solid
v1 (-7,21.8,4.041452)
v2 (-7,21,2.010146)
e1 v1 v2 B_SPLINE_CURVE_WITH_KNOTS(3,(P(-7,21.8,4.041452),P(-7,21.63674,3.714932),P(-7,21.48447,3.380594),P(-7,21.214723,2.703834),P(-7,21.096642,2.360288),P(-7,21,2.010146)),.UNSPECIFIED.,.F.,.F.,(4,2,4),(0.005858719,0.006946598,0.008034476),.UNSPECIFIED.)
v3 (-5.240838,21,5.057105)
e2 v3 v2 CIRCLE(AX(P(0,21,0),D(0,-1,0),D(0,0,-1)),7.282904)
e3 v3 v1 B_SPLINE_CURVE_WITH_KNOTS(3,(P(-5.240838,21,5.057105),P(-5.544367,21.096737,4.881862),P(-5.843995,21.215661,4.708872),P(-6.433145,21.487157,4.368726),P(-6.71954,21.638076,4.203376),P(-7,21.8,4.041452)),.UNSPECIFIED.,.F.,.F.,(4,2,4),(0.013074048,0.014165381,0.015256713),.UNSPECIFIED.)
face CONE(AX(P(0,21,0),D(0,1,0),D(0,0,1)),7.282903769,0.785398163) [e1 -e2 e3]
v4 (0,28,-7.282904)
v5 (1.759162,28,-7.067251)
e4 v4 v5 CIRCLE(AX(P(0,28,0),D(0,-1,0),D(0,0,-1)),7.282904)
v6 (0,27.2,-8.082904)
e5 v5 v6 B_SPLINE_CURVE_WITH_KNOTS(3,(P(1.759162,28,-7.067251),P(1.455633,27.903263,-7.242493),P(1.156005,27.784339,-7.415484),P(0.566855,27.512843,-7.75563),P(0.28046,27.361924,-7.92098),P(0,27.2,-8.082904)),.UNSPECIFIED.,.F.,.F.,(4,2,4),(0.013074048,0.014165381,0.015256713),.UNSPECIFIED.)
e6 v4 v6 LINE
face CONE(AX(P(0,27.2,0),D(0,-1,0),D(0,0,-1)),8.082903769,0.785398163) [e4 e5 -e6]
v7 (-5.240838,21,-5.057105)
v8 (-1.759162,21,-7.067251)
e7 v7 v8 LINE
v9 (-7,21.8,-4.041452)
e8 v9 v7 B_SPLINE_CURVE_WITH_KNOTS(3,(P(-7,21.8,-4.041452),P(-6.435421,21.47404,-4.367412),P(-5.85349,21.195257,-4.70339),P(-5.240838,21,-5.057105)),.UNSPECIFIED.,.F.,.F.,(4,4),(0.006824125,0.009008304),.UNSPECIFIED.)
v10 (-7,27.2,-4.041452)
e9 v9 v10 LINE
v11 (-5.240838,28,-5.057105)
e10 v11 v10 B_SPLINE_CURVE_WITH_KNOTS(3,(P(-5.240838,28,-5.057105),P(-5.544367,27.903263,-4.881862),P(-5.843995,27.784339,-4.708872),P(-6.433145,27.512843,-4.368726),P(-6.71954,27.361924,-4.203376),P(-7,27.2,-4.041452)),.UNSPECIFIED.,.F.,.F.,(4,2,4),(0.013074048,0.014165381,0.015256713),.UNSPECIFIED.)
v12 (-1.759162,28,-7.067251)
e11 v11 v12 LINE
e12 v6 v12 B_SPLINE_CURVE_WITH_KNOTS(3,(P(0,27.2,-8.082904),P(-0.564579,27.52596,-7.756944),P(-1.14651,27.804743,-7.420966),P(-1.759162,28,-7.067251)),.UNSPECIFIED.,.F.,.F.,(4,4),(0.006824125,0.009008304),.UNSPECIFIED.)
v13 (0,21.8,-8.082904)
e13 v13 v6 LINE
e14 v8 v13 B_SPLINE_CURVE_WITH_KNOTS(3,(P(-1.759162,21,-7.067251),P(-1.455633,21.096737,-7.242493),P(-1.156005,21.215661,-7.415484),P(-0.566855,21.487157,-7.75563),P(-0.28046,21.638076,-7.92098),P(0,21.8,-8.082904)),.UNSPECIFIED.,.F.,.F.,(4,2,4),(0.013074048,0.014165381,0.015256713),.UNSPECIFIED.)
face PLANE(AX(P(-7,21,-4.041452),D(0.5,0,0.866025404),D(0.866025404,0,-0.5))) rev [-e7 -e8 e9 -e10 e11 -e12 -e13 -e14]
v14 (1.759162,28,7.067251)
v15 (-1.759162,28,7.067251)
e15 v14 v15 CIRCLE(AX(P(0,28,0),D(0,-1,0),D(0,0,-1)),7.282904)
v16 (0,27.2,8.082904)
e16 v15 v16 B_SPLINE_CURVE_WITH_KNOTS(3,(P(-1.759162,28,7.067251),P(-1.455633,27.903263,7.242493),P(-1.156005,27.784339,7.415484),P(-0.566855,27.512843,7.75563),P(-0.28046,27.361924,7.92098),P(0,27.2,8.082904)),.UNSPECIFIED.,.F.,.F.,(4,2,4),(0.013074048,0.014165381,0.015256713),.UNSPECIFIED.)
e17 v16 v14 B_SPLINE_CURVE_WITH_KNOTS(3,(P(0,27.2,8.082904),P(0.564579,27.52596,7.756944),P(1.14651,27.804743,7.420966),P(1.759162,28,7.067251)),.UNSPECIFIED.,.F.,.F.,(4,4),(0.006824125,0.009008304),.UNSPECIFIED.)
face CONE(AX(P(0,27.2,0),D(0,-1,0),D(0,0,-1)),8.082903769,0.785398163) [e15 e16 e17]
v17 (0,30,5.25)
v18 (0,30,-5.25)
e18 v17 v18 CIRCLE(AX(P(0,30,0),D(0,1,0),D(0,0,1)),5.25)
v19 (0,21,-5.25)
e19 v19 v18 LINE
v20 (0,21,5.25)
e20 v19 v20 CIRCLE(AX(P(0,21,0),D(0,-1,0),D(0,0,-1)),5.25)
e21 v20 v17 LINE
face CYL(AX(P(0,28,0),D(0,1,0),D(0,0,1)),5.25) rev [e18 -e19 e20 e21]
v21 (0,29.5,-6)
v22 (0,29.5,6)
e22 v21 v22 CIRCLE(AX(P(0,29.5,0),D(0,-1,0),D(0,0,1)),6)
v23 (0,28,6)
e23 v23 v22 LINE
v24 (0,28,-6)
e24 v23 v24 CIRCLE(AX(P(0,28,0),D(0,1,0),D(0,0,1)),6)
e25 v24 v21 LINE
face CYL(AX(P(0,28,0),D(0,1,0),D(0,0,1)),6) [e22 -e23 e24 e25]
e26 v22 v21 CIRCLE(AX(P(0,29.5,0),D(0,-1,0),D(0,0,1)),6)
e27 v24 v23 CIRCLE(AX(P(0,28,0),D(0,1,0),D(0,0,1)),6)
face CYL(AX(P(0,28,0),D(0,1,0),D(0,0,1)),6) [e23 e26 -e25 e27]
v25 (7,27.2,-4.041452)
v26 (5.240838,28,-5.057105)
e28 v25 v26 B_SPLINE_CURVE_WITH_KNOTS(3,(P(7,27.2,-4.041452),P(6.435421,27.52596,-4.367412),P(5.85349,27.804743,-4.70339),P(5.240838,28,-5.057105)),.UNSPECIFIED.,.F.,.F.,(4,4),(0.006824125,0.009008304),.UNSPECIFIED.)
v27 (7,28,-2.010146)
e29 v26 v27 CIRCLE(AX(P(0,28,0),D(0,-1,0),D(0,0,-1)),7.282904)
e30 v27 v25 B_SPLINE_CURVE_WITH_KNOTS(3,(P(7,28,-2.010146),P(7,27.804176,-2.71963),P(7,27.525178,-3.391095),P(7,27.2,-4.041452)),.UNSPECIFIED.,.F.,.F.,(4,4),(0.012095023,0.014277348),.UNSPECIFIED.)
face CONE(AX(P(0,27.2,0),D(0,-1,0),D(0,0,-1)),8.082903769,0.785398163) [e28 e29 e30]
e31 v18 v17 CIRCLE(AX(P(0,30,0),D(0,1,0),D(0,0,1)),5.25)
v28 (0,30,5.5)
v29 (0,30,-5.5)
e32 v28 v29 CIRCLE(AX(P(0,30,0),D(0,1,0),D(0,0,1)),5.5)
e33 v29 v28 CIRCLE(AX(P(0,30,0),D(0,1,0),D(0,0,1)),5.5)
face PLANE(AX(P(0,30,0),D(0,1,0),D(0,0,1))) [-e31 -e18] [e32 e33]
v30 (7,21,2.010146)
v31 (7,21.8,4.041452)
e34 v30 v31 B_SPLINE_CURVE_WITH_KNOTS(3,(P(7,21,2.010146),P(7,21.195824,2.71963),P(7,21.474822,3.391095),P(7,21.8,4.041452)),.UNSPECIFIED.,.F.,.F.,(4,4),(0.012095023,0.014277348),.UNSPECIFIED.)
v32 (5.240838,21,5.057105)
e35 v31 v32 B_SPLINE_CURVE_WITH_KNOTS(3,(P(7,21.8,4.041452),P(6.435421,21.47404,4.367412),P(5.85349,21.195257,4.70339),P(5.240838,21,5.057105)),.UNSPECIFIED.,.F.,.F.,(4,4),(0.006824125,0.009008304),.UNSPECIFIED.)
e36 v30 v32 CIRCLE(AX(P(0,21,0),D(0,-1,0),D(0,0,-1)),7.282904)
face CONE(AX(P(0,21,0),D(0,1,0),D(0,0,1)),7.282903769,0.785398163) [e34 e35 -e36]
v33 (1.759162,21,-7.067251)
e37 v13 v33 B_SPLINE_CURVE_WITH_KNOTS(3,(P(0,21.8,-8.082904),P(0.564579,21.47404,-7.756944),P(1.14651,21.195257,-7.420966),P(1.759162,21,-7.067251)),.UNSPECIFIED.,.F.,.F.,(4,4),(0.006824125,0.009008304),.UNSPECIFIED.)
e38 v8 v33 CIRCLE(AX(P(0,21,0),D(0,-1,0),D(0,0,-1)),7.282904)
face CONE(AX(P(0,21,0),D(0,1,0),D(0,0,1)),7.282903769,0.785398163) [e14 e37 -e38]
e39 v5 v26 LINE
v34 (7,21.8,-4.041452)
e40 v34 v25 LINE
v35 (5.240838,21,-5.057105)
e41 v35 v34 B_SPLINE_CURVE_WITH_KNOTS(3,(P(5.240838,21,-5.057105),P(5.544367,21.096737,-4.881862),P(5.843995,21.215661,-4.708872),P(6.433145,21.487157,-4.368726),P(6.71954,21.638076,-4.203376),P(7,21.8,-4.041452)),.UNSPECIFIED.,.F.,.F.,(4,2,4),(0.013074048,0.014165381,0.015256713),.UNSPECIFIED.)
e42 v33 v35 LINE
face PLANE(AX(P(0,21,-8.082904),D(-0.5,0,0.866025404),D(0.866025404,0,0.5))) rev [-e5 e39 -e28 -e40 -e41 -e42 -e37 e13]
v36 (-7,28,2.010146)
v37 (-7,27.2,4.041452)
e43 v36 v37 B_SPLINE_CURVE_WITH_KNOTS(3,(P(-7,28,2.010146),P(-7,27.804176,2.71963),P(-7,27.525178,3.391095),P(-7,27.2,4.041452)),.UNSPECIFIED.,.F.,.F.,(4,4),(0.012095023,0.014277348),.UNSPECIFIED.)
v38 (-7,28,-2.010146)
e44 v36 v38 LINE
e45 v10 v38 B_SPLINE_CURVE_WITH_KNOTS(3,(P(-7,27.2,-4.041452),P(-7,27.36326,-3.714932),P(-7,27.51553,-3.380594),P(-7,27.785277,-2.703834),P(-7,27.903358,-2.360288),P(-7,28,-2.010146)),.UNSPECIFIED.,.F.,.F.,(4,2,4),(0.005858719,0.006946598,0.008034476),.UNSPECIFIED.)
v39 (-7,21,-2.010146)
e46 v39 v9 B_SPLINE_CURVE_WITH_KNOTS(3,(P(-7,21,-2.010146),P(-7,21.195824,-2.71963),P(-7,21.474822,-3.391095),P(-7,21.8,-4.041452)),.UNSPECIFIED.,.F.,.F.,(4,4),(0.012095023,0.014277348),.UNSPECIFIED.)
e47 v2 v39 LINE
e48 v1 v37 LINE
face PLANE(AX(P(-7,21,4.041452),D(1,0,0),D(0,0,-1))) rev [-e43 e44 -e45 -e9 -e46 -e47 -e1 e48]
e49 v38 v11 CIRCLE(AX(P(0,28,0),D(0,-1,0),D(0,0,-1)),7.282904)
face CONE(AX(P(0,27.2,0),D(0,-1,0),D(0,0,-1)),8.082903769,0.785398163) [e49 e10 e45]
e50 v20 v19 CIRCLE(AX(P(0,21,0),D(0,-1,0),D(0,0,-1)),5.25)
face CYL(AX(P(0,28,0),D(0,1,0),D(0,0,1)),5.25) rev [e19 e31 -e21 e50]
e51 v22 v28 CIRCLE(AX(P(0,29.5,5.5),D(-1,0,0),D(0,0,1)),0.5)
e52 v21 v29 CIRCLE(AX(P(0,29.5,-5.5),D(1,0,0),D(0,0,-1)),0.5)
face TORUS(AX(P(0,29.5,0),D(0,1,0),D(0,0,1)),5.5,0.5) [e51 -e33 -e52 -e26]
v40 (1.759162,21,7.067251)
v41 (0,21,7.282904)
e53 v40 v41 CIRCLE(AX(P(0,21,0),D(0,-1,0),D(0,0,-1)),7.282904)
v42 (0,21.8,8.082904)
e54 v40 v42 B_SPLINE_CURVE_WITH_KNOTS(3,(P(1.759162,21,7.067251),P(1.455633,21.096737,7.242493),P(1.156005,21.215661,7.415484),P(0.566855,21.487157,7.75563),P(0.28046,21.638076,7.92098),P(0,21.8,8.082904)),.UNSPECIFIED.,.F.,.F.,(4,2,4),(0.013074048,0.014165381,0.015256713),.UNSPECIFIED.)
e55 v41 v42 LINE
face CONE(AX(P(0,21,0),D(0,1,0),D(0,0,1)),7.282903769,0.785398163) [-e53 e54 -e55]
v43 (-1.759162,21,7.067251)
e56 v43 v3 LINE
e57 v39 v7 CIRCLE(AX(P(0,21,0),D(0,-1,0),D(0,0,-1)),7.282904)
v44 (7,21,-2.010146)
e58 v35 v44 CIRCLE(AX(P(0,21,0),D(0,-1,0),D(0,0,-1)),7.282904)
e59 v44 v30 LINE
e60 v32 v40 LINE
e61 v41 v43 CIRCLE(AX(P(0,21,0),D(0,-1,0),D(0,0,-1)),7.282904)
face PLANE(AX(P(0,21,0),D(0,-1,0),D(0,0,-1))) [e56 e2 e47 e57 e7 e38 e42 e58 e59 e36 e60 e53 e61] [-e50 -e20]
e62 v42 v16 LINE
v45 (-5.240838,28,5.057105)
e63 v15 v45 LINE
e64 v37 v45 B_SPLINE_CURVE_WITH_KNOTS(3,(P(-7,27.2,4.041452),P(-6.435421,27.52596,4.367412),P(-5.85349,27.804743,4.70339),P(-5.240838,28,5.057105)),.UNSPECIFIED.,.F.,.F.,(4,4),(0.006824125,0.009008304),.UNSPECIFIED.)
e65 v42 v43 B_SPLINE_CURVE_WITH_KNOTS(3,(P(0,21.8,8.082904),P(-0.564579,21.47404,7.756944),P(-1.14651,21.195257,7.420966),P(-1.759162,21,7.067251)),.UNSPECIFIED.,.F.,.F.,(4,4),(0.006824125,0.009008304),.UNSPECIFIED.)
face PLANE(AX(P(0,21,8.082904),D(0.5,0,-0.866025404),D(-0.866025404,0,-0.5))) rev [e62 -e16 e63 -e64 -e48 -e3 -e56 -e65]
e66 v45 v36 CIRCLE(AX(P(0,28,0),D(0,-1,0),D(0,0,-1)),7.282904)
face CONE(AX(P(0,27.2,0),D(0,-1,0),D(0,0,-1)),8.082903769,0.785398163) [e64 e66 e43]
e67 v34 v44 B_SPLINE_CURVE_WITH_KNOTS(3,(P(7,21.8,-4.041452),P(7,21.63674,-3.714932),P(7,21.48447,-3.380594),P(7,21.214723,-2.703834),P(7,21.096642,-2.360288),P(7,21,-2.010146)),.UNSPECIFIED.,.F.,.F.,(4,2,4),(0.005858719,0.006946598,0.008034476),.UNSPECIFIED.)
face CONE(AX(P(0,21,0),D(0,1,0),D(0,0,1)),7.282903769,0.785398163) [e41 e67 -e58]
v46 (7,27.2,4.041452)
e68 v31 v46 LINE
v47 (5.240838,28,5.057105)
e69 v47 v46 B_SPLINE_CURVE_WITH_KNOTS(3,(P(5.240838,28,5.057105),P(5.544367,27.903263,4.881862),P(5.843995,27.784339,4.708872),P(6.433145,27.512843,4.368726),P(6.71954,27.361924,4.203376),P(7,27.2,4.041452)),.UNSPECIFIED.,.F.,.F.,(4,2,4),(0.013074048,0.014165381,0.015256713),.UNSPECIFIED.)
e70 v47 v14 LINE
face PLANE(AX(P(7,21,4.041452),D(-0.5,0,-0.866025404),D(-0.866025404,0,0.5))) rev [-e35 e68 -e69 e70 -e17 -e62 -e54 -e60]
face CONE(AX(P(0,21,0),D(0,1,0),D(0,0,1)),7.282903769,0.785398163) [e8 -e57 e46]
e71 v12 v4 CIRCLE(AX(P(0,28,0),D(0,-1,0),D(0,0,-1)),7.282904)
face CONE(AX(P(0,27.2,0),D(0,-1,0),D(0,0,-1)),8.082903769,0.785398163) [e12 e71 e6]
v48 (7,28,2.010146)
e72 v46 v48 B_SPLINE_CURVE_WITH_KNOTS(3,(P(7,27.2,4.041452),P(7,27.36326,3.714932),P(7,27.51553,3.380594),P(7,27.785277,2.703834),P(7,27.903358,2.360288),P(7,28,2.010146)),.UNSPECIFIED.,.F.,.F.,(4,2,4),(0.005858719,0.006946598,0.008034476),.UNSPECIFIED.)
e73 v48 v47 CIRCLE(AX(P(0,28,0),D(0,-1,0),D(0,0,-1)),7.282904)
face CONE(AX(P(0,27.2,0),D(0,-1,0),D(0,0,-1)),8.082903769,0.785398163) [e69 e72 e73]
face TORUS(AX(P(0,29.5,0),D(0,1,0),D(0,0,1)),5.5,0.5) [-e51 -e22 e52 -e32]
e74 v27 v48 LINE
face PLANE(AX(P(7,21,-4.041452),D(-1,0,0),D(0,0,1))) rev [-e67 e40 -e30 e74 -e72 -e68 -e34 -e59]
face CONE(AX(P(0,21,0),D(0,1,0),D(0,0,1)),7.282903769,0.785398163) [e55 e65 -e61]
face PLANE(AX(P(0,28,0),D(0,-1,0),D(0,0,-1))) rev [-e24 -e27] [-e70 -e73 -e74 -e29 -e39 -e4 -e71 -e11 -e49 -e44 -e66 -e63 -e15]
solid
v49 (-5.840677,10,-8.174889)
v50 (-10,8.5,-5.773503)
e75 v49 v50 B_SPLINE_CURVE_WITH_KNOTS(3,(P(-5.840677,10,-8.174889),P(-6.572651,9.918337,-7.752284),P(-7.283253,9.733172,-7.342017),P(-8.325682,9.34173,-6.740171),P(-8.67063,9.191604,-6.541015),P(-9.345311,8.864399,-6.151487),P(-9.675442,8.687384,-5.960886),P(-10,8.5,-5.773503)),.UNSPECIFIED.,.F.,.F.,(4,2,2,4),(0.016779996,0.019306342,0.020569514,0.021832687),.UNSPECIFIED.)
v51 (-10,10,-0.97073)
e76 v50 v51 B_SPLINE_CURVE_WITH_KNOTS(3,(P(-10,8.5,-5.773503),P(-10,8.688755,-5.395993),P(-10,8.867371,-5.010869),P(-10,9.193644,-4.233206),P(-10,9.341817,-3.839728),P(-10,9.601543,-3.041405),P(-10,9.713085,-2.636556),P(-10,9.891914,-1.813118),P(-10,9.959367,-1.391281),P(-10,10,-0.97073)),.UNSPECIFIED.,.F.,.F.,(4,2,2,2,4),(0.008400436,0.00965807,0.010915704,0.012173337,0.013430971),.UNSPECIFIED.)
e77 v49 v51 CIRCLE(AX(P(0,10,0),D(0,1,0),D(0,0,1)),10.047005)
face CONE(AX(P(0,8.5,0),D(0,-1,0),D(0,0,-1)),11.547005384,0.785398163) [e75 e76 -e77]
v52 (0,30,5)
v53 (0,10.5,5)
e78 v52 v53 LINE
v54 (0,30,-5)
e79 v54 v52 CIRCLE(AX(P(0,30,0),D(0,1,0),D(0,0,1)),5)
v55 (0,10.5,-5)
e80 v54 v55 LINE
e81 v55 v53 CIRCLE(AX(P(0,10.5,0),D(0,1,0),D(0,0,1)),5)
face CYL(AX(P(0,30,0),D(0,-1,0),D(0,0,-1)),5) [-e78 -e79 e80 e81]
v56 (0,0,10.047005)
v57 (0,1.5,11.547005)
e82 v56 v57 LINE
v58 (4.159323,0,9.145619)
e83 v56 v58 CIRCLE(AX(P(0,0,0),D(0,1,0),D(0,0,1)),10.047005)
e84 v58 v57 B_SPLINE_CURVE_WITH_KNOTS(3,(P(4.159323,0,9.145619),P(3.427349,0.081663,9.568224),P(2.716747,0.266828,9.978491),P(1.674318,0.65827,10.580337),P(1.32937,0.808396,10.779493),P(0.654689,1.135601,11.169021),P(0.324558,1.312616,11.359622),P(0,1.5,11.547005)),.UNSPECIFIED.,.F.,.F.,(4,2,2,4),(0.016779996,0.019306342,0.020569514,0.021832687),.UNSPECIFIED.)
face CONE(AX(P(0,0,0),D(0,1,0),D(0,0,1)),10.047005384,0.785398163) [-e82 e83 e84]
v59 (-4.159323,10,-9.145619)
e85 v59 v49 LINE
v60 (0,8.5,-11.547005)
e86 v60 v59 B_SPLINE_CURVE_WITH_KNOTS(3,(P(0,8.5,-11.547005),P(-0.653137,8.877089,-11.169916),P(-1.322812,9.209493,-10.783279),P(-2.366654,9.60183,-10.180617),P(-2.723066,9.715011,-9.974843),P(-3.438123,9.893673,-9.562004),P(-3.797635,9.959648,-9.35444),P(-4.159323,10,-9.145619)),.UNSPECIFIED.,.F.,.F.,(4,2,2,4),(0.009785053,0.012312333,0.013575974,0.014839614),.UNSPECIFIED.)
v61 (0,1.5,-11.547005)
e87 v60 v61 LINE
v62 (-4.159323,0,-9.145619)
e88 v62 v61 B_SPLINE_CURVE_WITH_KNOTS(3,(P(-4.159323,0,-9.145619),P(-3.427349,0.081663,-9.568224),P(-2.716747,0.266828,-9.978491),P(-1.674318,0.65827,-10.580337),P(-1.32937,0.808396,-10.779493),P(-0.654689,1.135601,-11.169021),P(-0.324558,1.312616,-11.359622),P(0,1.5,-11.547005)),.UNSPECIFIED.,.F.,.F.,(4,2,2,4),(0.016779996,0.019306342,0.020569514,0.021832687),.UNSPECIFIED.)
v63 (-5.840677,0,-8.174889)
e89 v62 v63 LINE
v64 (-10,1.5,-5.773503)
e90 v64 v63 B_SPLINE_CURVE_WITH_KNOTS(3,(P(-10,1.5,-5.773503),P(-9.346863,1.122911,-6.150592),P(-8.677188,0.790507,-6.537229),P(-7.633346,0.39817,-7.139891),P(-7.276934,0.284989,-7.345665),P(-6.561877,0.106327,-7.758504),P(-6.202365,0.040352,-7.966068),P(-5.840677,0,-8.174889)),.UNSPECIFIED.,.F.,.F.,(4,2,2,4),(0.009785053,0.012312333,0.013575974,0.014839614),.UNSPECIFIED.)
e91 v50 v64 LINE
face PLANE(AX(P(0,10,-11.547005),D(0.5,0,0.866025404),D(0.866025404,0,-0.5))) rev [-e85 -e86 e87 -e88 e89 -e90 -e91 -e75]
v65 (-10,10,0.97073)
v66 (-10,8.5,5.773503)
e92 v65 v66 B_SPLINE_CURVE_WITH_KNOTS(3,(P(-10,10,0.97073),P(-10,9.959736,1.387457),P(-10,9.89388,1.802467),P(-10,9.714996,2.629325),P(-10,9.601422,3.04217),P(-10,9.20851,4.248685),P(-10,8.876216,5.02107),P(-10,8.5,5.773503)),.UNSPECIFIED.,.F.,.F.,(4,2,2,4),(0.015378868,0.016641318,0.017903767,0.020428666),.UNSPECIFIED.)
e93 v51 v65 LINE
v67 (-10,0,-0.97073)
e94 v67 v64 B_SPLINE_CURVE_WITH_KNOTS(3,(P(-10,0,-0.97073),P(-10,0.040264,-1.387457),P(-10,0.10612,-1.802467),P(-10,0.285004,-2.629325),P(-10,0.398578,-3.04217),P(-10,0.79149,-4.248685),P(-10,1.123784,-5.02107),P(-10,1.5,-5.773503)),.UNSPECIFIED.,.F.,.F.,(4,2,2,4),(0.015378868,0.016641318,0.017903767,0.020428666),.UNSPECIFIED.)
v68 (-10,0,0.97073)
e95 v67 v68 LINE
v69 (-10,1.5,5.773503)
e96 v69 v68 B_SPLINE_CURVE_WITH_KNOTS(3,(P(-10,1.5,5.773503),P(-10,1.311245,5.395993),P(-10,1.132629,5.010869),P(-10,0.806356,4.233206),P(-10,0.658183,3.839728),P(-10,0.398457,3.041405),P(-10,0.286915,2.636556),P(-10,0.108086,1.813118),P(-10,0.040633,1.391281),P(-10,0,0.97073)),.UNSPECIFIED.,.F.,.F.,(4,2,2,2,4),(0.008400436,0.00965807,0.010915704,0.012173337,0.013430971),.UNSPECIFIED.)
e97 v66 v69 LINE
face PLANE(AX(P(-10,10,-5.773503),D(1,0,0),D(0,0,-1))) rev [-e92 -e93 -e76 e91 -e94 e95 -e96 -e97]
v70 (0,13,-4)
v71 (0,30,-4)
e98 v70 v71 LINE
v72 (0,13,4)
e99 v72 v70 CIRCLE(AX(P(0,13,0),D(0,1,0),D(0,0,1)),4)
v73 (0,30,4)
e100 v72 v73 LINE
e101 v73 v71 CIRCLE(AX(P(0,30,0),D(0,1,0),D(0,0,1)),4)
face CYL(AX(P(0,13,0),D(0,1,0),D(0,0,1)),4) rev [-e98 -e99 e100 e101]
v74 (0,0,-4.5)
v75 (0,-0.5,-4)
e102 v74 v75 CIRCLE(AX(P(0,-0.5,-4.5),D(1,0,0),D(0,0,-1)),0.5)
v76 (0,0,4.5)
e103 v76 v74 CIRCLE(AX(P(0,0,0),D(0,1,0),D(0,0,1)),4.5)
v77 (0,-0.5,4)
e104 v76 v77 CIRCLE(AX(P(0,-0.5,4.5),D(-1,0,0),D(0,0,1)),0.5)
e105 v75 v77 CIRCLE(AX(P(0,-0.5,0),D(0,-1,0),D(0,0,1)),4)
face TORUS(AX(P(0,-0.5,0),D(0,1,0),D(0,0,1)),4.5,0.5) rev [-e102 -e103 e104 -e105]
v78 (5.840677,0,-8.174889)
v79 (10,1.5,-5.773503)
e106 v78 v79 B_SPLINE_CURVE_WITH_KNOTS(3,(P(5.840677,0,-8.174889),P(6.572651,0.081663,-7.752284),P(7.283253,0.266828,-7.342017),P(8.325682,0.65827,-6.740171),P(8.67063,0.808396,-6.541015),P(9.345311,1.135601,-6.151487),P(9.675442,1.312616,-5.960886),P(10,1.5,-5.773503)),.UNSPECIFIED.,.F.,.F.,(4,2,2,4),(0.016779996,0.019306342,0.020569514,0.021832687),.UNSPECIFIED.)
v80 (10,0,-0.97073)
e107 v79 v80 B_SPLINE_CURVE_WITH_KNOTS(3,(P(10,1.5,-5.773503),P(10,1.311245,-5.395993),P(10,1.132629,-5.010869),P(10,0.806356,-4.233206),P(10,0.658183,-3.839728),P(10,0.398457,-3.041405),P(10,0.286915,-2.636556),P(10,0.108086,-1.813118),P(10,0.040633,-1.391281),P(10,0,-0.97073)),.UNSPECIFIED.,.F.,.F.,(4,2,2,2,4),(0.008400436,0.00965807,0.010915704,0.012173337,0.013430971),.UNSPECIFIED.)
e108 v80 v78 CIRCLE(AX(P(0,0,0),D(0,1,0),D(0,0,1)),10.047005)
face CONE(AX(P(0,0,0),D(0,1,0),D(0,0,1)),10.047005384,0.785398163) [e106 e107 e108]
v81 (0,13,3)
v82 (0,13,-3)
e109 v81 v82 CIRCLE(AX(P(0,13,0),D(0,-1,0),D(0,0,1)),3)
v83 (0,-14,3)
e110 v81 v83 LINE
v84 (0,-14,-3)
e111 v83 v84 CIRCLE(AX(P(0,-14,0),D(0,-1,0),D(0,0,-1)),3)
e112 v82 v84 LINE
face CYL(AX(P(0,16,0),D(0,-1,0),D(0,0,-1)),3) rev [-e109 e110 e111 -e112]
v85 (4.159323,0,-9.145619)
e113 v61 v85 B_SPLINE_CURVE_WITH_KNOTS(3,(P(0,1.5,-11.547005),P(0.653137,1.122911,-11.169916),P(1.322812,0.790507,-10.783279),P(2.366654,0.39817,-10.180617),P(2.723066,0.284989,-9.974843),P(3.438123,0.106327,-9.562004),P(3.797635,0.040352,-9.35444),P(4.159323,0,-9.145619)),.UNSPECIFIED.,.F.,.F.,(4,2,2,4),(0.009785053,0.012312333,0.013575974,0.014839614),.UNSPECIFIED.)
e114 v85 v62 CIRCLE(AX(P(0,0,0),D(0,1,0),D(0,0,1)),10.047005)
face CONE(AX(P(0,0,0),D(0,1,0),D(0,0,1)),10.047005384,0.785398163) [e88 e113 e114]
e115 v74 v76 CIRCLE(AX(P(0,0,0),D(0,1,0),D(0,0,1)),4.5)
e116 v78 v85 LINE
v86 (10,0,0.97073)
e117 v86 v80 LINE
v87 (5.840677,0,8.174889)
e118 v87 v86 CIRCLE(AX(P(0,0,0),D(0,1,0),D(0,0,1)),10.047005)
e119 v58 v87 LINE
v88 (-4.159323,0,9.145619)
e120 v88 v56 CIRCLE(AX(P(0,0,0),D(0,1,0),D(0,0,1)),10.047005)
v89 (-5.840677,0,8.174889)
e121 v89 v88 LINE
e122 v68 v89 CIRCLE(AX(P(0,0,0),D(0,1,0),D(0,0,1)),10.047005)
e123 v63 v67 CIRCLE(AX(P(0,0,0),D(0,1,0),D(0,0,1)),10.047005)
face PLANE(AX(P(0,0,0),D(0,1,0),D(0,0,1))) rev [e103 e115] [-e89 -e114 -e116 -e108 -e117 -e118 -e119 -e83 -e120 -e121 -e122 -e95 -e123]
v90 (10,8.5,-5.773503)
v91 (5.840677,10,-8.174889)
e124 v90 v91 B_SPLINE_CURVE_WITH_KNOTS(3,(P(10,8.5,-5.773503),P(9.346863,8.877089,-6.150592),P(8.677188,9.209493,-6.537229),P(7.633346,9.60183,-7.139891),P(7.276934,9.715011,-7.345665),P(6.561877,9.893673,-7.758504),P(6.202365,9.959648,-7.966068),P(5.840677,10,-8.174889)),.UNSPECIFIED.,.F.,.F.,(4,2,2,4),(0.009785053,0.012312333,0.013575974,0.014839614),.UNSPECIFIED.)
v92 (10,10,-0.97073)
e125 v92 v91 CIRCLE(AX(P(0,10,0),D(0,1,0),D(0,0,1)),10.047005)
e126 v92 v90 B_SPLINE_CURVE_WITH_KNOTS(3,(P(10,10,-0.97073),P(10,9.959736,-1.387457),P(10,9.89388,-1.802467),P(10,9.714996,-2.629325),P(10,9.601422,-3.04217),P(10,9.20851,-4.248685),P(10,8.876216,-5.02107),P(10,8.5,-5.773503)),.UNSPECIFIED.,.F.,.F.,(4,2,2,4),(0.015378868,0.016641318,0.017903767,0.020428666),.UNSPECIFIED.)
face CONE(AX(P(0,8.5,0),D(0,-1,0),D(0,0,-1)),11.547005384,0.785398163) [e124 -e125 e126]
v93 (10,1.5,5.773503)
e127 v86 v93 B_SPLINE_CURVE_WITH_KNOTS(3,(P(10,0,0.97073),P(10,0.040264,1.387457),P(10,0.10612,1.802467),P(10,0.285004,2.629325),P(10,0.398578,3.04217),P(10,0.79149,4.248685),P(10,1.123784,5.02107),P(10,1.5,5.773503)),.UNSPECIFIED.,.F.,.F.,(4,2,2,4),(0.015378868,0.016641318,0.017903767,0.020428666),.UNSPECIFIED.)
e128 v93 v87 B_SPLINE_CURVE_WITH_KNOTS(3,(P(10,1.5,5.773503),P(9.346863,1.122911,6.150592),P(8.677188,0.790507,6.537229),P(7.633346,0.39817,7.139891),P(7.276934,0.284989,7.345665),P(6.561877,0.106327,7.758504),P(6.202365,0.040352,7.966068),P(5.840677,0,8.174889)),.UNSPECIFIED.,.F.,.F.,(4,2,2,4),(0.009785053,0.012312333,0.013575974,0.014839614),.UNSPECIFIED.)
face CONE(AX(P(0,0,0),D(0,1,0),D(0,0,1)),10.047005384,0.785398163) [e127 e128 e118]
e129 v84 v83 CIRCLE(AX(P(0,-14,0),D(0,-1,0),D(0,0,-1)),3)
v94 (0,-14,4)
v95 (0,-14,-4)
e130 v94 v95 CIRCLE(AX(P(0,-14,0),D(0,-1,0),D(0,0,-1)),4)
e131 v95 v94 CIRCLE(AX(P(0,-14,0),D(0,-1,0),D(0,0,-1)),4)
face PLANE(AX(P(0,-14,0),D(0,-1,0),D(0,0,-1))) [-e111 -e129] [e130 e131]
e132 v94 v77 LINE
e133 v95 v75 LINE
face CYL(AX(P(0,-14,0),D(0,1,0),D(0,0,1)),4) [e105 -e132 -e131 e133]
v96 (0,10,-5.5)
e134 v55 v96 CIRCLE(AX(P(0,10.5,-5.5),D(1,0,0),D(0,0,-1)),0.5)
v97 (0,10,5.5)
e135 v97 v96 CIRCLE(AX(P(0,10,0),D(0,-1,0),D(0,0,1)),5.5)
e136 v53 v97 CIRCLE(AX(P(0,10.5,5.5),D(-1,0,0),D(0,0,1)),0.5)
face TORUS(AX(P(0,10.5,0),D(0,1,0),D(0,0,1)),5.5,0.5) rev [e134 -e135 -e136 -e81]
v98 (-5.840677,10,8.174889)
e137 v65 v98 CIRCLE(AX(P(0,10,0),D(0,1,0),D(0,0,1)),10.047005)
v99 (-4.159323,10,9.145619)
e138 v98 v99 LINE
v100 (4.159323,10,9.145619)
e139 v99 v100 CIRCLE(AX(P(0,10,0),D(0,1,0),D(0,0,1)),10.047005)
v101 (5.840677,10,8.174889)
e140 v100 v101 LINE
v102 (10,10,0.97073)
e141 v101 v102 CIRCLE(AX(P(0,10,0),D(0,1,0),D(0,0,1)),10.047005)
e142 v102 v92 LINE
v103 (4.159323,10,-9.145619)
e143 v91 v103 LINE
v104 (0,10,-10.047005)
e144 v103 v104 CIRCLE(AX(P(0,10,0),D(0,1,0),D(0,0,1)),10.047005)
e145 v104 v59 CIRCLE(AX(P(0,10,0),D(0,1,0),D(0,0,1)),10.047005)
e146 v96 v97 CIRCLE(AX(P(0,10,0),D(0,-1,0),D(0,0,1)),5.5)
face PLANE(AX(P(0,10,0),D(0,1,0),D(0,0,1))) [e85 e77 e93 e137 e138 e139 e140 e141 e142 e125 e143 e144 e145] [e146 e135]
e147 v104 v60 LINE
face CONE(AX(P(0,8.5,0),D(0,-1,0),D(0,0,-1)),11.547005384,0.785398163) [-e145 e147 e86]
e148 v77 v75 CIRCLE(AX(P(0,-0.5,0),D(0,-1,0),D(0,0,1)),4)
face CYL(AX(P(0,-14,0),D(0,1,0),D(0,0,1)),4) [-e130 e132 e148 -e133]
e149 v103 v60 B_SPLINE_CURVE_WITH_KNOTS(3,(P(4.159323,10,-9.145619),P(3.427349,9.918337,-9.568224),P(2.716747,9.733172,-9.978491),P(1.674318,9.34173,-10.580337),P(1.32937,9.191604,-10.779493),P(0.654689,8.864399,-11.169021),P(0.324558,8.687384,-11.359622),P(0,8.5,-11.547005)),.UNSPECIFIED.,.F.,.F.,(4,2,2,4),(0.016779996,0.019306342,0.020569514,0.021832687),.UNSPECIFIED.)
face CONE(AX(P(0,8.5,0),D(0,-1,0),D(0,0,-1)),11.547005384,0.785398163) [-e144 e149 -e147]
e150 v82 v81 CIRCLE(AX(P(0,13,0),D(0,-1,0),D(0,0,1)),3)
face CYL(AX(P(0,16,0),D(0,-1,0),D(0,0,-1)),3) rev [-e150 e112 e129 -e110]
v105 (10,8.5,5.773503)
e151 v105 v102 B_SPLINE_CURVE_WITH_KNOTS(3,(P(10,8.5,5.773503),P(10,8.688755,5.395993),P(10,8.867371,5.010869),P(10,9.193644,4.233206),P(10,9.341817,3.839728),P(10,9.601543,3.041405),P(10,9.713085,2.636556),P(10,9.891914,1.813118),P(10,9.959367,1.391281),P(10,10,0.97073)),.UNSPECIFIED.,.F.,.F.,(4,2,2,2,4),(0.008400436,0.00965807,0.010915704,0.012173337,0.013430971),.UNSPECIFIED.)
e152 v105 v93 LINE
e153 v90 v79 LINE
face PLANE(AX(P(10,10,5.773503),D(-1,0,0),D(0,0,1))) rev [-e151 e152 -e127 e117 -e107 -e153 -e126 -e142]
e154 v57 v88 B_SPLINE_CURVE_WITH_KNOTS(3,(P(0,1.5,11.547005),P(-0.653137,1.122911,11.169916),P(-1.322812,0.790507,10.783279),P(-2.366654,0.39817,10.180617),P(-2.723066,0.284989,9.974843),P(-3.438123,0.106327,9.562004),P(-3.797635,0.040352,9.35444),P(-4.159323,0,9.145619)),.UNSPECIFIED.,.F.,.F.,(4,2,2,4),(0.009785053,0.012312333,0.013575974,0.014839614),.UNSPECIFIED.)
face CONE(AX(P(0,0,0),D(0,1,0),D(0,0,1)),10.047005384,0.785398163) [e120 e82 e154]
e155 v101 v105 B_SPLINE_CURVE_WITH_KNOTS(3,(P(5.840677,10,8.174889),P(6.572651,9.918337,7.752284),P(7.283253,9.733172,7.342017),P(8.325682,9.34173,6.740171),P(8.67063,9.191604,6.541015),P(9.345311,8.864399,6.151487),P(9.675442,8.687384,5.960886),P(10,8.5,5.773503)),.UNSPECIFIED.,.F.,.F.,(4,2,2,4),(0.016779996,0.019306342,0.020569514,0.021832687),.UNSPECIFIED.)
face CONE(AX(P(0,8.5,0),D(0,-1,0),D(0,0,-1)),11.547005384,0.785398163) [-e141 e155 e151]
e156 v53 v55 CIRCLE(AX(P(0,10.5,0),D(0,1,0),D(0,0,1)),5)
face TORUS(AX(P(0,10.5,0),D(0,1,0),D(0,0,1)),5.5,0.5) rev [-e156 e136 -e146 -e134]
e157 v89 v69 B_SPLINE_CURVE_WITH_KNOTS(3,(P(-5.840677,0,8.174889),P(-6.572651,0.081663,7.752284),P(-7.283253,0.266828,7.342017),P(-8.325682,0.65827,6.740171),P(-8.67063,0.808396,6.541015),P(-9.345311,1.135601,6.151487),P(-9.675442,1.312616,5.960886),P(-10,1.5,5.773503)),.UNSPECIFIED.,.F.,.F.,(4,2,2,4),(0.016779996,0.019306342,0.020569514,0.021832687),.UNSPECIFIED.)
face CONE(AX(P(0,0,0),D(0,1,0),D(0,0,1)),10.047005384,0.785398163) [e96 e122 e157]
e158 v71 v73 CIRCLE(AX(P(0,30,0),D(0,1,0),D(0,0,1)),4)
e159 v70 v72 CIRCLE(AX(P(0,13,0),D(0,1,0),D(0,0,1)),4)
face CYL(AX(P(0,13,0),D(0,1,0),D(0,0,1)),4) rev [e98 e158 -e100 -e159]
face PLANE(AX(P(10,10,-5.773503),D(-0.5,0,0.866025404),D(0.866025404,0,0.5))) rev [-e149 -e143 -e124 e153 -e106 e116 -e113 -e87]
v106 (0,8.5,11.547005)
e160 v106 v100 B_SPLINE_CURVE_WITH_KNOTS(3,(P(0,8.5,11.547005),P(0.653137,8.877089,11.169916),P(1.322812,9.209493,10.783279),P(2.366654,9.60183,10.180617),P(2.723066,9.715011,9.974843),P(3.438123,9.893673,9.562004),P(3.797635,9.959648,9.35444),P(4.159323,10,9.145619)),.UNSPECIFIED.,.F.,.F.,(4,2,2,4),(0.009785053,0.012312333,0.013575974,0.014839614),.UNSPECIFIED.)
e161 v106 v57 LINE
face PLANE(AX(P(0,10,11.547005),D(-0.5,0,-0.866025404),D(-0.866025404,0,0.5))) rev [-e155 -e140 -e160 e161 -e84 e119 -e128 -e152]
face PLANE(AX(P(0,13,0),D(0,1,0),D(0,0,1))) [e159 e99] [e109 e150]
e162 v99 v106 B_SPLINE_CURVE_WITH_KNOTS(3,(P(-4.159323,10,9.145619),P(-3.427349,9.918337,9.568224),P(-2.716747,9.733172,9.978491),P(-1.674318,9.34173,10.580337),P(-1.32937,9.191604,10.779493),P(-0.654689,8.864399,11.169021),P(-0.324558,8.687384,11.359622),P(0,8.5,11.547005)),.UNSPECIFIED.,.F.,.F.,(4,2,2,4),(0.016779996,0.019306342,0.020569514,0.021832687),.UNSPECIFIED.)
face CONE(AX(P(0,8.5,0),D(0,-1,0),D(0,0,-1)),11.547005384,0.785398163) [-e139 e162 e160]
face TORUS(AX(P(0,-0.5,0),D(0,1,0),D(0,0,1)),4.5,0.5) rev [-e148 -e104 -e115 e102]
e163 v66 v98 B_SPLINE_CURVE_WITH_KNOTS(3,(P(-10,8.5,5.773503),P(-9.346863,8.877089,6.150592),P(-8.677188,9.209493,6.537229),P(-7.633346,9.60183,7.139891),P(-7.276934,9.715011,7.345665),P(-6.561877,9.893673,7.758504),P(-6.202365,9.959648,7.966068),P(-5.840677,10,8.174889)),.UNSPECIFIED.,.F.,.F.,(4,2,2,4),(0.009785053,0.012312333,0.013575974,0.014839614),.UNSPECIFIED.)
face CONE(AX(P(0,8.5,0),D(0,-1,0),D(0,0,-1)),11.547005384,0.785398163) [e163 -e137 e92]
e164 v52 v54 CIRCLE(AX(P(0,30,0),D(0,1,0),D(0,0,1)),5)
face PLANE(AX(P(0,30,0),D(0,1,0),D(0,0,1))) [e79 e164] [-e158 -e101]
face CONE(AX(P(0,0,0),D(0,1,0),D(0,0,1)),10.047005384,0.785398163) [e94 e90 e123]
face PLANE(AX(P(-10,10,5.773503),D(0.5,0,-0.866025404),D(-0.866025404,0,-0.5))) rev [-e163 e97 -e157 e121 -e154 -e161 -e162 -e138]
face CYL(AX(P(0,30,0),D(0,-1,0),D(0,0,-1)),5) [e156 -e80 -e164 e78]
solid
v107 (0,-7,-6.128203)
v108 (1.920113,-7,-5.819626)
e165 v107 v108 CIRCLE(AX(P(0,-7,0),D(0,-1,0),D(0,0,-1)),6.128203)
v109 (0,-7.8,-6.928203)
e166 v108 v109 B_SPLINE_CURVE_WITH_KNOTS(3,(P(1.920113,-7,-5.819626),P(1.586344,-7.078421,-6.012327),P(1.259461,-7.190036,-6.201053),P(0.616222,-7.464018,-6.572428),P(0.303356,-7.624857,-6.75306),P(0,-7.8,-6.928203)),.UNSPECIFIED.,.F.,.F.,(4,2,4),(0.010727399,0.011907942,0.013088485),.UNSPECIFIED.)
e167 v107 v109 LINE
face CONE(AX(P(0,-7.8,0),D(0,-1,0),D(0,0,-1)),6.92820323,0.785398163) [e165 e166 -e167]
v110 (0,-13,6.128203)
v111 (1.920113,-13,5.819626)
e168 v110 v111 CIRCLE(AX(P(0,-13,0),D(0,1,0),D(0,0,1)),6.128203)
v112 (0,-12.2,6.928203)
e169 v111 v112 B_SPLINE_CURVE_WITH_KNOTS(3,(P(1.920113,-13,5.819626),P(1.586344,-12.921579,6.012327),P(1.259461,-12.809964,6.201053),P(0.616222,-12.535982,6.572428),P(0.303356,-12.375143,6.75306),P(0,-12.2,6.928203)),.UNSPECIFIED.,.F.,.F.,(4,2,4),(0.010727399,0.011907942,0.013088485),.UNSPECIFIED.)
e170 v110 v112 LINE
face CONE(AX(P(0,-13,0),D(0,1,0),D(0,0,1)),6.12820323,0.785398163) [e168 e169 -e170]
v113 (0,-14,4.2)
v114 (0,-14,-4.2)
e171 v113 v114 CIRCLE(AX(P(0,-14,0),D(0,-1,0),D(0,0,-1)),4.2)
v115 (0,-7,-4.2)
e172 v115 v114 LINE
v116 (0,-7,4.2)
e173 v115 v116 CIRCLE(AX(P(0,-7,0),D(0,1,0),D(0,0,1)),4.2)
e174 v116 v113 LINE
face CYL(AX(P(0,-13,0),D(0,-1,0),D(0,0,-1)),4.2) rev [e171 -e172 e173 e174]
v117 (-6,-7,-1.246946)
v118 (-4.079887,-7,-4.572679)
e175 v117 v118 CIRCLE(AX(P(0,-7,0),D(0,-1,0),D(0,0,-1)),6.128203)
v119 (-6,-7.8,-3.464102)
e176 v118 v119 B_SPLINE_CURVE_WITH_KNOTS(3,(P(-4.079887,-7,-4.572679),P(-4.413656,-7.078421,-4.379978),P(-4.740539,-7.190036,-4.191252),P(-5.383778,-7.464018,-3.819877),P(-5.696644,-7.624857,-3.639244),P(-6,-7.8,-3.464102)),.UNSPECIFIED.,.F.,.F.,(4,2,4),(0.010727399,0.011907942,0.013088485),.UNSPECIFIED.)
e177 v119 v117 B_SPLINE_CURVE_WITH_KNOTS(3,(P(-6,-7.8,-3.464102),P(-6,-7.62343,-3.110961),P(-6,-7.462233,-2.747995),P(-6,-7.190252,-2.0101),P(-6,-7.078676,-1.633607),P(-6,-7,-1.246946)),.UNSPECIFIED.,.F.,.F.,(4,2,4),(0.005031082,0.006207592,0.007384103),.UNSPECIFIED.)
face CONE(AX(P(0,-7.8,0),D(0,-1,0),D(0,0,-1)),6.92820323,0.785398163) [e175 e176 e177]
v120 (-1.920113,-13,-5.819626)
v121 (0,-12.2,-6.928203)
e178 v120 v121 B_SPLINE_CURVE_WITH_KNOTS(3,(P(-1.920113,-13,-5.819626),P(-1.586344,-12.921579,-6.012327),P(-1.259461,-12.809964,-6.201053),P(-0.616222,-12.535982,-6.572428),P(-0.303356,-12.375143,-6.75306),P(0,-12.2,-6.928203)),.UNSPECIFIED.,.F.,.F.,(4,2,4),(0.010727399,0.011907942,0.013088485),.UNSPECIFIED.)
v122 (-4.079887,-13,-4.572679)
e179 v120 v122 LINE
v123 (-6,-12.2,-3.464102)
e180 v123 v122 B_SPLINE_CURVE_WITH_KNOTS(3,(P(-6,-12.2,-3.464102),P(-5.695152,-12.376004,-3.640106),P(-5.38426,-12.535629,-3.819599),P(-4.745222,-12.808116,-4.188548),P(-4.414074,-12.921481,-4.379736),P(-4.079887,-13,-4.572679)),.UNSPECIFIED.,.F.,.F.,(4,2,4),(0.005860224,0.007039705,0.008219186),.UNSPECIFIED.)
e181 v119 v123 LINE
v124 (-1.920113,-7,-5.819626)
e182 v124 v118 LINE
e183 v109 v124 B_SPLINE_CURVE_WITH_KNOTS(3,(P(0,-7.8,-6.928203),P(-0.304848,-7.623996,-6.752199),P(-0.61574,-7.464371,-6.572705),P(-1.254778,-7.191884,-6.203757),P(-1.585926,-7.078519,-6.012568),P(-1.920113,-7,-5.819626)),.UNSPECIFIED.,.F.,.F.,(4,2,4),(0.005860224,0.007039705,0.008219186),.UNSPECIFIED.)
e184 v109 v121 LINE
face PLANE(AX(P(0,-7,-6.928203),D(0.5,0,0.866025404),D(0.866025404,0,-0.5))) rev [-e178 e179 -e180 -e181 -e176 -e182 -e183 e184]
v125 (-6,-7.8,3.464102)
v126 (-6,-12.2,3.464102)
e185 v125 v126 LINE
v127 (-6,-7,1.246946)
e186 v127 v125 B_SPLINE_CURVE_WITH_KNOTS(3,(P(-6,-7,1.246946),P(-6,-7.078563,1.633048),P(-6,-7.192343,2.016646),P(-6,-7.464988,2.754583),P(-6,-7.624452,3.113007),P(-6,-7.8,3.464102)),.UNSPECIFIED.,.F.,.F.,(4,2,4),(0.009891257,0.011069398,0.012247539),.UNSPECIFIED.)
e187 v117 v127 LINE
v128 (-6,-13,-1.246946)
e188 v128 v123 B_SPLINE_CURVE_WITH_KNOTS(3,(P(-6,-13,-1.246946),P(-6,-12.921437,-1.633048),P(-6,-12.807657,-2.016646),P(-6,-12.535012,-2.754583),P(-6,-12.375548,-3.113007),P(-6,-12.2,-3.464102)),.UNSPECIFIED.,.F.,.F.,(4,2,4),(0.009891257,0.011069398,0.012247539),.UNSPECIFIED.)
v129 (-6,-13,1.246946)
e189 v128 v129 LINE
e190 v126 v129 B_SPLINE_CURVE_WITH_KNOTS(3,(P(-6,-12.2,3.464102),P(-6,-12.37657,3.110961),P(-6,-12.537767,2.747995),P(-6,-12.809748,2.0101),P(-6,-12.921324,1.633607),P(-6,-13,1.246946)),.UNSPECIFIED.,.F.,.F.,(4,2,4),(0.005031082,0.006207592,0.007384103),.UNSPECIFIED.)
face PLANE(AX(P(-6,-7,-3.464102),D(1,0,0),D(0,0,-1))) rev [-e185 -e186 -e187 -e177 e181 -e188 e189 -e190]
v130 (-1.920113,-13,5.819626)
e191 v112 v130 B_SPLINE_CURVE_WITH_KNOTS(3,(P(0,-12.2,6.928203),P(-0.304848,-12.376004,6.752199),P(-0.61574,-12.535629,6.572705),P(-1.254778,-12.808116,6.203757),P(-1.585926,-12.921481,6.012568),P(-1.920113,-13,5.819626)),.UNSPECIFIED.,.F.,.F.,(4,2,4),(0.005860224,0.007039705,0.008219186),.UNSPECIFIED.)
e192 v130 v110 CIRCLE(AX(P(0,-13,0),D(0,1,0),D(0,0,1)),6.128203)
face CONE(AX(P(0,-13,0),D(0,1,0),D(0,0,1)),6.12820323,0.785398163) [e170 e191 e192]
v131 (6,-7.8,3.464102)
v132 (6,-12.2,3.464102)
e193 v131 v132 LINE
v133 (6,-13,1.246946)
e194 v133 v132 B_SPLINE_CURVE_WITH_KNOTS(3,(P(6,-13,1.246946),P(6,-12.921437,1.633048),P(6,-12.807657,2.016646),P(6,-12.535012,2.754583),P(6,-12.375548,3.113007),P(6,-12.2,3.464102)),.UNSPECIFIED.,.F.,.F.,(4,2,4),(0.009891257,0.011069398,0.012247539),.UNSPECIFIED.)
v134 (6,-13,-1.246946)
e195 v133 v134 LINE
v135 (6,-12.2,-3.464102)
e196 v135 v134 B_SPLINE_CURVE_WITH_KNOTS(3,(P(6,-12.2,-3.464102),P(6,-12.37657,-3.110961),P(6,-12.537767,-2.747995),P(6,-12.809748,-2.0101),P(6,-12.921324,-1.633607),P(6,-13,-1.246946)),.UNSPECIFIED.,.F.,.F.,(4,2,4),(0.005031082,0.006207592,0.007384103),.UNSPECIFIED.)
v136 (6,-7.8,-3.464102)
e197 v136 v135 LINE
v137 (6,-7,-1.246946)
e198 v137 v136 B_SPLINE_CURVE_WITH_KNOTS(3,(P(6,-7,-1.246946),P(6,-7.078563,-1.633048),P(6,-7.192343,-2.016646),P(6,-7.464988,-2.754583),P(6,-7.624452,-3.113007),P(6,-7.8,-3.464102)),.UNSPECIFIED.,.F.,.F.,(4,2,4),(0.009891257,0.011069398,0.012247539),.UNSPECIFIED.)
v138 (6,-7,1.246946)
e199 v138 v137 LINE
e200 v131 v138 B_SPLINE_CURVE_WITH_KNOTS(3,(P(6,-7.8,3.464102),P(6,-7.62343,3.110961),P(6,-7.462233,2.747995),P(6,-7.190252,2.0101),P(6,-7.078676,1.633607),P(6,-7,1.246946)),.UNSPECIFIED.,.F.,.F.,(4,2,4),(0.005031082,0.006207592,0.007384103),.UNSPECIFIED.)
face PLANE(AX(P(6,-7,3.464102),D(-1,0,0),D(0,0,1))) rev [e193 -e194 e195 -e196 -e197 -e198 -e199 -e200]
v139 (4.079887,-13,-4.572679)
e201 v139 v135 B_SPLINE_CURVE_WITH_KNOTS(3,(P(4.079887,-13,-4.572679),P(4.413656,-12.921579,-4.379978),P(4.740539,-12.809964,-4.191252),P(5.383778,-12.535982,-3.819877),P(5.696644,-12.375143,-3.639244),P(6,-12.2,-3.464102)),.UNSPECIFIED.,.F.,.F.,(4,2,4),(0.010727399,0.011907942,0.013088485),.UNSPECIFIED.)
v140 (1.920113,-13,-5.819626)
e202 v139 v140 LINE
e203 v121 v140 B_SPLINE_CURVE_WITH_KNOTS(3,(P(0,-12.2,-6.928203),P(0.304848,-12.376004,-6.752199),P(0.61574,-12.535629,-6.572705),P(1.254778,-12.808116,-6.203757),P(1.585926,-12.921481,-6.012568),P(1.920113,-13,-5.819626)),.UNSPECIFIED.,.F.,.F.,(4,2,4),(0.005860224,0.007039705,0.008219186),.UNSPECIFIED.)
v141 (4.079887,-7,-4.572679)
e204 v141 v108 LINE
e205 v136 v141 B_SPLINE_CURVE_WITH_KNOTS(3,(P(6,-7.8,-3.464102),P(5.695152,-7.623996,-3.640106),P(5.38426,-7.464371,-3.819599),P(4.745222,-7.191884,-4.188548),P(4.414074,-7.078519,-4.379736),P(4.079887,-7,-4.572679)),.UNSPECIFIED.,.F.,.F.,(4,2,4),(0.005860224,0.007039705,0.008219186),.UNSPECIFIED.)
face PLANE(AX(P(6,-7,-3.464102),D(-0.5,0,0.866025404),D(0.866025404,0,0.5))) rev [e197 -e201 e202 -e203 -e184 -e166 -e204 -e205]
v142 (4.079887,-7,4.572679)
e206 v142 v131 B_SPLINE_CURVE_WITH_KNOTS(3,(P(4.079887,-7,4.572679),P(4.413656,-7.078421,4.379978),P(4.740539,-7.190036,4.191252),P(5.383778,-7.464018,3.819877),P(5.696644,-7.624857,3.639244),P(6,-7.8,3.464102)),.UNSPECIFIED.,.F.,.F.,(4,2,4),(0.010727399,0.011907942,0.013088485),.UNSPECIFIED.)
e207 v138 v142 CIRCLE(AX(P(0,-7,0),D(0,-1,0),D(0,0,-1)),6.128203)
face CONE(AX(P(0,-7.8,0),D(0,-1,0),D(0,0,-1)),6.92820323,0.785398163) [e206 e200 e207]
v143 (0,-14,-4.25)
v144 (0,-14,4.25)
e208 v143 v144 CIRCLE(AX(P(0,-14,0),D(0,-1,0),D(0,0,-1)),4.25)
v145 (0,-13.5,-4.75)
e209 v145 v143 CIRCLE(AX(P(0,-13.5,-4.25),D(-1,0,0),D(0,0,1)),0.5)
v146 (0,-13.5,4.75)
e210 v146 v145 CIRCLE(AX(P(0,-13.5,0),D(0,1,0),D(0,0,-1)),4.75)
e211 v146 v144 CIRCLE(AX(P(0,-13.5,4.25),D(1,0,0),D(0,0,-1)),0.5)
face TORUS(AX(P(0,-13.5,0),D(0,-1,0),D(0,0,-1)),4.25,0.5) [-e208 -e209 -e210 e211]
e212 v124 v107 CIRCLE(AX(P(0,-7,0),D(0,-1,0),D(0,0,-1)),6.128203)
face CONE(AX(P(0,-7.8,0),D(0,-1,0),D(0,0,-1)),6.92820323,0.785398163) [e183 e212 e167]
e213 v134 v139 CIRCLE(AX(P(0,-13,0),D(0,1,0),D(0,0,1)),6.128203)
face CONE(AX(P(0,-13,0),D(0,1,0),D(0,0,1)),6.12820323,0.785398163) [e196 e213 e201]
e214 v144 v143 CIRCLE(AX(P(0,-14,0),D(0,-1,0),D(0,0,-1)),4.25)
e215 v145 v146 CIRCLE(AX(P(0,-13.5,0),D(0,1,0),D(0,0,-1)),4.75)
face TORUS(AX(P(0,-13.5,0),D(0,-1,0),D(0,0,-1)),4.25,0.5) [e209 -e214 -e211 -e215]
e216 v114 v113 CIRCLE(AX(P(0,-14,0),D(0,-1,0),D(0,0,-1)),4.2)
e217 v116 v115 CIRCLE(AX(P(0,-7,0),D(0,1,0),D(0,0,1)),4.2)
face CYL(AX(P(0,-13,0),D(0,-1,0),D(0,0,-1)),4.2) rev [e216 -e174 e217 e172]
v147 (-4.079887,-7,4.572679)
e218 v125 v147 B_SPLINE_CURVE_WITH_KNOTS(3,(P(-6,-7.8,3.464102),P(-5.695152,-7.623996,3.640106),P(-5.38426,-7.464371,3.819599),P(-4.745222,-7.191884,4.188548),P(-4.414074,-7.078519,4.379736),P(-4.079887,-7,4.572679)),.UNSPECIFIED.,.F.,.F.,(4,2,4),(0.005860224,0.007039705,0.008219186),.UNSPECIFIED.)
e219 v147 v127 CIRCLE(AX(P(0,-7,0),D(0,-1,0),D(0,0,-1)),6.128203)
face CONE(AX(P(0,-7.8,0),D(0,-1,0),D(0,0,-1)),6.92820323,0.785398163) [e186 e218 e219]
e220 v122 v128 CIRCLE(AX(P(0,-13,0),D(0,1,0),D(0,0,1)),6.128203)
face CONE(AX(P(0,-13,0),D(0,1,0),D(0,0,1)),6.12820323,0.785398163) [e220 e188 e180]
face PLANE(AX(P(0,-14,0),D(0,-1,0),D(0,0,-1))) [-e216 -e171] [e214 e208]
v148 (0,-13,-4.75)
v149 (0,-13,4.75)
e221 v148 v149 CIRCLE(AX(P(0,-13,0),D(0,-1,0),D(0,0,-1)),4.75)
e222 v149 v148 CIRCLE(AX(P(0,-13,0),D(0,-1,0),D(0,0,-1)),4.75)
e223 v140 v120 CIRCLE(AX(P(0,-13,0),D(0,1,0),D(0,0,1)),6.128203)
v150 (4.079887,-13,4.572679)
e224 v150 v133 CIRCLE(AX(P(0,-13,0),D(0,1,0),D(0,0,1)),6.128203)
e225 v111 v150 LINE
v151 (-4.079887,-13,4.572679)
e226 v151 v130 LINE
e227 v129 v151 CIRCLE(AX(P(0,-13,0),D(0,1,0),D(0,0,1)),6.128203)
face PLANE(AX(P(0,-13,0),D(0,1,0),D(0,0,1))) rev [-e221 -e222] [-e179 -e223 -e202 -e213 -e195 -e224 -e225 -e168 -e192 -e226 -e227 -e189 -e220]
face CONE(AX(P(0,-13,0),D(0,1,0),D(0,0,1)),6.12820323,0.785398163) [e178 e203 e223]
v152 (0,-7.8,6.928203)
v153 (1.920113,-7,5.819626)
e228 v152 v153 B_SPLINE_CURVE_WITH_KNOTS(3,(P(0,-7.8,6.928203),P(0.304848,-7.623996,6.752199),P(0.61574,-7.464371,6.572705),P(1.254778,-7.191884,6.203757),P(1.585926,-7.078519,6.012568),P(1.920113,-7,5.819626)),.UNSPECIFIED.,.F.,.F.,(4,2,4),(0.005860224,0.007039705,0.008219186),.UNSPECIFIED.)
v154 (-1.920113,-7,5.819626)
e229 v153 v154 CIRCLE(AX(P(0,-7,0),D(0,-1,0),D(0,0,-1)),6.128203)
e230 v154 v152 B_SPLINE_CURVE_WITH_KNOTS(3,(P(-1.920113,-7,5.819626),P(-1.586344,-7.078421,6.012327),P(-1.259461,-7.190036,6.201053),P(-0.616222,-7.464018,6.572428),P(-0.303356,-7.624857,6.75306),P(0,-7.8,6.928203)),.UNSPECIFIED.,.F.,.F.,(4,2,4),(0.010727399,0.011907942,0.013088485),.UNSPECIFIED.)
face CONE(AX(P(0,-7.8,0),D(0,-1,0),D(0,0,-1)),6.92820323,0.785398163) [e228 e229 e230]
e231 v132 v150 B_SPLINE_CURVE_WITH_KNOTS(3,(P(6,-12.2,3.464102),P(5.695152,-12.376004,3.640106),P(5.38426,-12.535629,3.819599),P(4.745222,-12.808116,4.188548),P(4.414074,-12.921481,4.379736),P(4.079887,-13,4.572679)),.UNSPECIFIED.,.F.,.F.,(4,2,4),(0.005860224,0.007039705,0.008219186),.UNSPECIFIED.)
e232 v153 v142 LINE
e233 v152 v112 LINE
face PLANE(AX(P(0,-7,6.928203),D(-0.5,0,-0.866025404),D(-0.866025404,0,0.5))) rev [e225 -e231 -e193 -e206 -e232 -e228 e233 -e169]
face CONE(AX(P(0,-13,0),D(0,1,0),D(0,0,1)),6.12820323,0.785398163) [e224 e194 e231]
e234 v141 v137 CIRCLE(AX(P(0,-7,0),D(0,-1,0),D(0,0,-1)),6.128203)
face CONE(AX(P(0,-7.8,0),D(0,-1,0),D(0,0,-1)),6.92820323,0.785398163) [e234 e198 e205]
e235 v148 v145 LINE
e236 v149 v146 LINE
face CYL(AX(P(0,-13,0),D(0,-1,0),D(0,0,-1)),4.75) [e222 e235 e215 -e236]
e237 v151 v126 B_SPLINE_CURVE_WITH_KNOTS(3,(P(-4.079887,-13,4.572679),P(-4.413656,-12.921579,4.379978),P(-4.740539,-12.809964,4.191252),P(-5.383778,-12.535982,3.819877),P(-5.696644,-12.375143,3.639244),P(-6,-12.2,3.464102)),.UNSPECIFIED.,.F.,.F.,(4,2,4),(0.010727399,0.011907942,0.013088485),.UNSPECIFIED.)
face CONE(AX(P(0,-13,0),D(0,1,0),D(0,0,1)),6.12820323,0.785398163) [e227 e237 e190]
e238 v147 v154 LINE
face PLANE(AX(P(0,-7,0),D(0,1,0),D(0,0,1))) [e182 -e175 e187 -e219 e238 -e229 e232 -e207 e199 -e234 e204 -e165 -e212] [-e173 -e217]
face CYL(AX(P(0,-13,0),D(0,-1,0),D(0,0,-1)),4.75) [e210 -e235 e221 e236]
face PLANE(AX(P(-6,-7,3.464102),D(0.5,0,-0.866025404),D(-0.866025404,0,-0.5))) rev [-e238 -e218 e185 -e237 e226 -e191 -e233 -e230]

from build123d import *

# Parameters (mm, degrees)
BOSS_EXTRUDE1_DEPTH = 10
SKETCH2_R           = 5
BOSS_EXTRUDE2_DEPTH = 20
SKETCH3_R           = 4
BOSS_EXTRUDE3_DEPTH = 14
SKETCH4_R           = 3
CUT_EXTRUDE1_DEPTH  = 30
SKETCH5_R           = 4
CUT_EXTRUDE2_DEPTH  = 17
SKETCH6_R           = 6
SKETCH6_R_2         = 5.25
BOSS_EXTRUDE4_DEPTH = 2
SKETCH7_R           = 5.25
BOSS_EXTRUDE5_DEPTH = 7
SKETCH11_R          = 4.75
SKETCH11_R_2        = 4.2
BOSS_EXTRUDE6_DEPTH = 1
SKETCH12_R          = 4.2
BOSS_EXTRUDE7_DEPTH = 6
FILLET1_R           = 0.5
FILLET2_R           = 0.5
FILLET3_R           = 0.5


with BuildPart() as part:
    # Sketch1 → Boss-Extrude1 (new body)
    with BuildSketch(Plane(origin=(0, 0, 0), x_dir=(1, 0, 0), z_dir=(0, 1, 0))):
        Polygon((0, -11.547005384), (10, -5.773502692), (10, 5.773502692), (0, 11.547005384), (-10, 5.773502692), (-10, -5.773502692), align=None)
    extrude(amount=BOSS_EXTRUDE1_DEPTH)

    # Sketch2 → Boss-Extrude2 (add)
    with BuildSketch(Plane(origin=(0, 10, 0), x_dir=(1, 0, 0), z_dir=(0, 1, 0))):
        with Locations(Location((0, 0, 0), (0, 0, 270))):
            Circle(SKETCH2_R)
    extrude(amount=BOSS_EXTRUDE2_DEPTH)

    # Sketch3 → Boss-Extrude3 (add)
    with BuildSketch(Plane.XZ):
        with Locations(Location((0, 0, 0), (0, 0, 270))):
            Circle(SKETCH3_R)
    extrude(amount=BOSS_EXTRUDE3_DEPTH)

    # Sketch4 → Cut-Extrude1 (cut)
    with BuildSketch(Plane.XZ.offset(14)):
        with Locations(Location((0, 0, 0), (0, 0, 270))):
            Circle(SKETCH4_R)
    extrude(amount=-CUT_EXTRUDE1_DEPTH, mode=Mode.SUBTRACT)

    # Sketch5 → Cut-Extrude2 (cut)
    with BuildSketch(Plane(origin=(0, 30, 0), x_dir=(1, 0, 0), z_dir=(0, 1, 0))):
        with Locations(Location((0, 0, 0), (0, 0, 90))):
            Circle(SKETCH5_R)
    extrude(amount=-CUT_EXTRUDE2_DEPTH, mode=Mode.SUBTRACT)


with BuildPart() as body_2:
    # Sketch6 → Boss-Extrude4 (new body)
    with BuildSketch(Plane(origin=(0, 30, 0), x_dir=(1, 0, 0), z_dir=(0, 1, 0))):
        with Locations(Location((0, 0, 0), (0, 0, 270))):
            Circle(SKETCH6_R)
        with Locations(Location((0, 0, 0), (0, 0, 270))):
            Circle(SKETCH6_R_2, mode=Mode.SUBTRACT)
    extrude(amount=-BOSS_EXTRUDE4_DEPTH)

    # Sketch7 → Boss-Extrude5 (add)
    with BuildSketch(Plane.XZ.offset(-28)):
        Polygon((0, 8.082903769), (-7, 4.041451884), (-7, -4.041451884), (0, -8.082903769), (7, -4.041451884), (7, 4.041451884), align=None)
        with Locations(Location((0, 0, 0), (0, 0, 90))):
            Circle(SKETCH7_R, mode=Mode.SUBTRACT)
    extrude(amount=BOSS_EXTRUDE5_DEPTH)


with BuildPart() as body_3:
    # Sketch11 → Boss-Extrude6 (new body)
    with BuildSketch(Plane.XZ.offset(14)):
        with Locations(Location((0, 0, 0), (0, 0, 270))):
            Circle(SKETCH11_R)
        with Locations(Location((0, 0, 0), (0, 0, 270))):
            Circle(SKETCH11_R_2, mode=Mode.SUBTRACT)
    extrude(amount=-BOSS_EXTRUDE6_DEPTH)

    # Sketch12 → Boss-Extrude7 (add)
    with BuildSketch(Plane(origin=(0, -13, 0), x_dir=(1, 0, 0), z_dir=(0, 1, 0))):
        Polygon((0, 6.92820323), (-6, 3.464101615), (-6, -3.464101615), (0, -6.92820323), (6, -3.464101615), (6, 3.464101615), align=None)
        with Locations(Location((0, 0, 0), (0, 0, 90))):
            Circle(SKETCH12_R, mode=Mode.SUBTRACT)
    extrude(amount=BOSS_EXTRUDE7_DEPTH)


with BuildPart() as cut_revolve2_tool:
    # Sketch9 → Cut-Revolve2 (revolve)
    with BuildSketch(Plane(origin=(0, 0, 0), x_dir=(0, 0, -1), z_dir=(1, 0, 0))):
        Polygon((-7.282903769, 28), (-8.082903769, 27.2), (-8.082903769, 28), align=None)
        Polygon((-8.082903769, 21), (-7.282903769, 21), (-8.082903769, 21.8), align=None)
        Polygon((-11.547005384, 10), (-11.547005384, 8.5), (-10.047005384, 10), align=None)
        Polygon((-10.047005384, 0), (-11.547005384, 0), (-11.547005384, 1.5), align=None)
        Polygon((-6.92820323, -7), (-6.92820323, -7.8), (-6.12820323, -7), align=None)
        Polygon((-6.12820323, -13), (-6.92820323, -13), (-6.92820323, -12.2), align=None)
    revolve(axis=Axis((0, 30, 0), (0, 1, 0)))


with BuildPart() as part_1:
    add(part.part)

    # Cut-Revolve2: cut by cut_revolve2_tool
    add(cut_revolve2_tool.part, mode=Mode.SUBTRACT)

    # Fillet2
    fillet2_edges = [part_1.edges().sort_by_distance(p)[0] for p in [
        (0, 10, -5),
        (0, 0, 4),
    ]]
    fillet(fillet2_edges, radius=FILLET2_R)


with BuildPart() as body_2_1:
    add(body_2.part)

    # Cut-Revolve2: cut by cut_revolve2_tool
    add(cut_revolve2_tool.part, mode=Mode.SUBTRACT)

    # Fillet1
    fillet1_edges = [body_2_1.edges().sort_by_distance(p)[0] for p in [
        (0, 30, -6),
    ]]
    fillet(fillet1_edges, radius=FILLET1_R)


with BuildPart() as body_3_1:
    add(body_3.part)

    # Cut-Revolve2: cut by cut_revolve2_tool
    add(cut_revolve2_tool.part, mode=Mode.SUBTRACT)

    # Fillet3
    fillet3_edges = [body_3_1.edges().sort_by_distance(p)[0] for p in [
        (0, -14, 4.75),
    ]]
    fillet(fillet3_edges, radius=FILLET3_R)


solid = Compound([part_1.part, body_2_1.part, body_3_1.part])
